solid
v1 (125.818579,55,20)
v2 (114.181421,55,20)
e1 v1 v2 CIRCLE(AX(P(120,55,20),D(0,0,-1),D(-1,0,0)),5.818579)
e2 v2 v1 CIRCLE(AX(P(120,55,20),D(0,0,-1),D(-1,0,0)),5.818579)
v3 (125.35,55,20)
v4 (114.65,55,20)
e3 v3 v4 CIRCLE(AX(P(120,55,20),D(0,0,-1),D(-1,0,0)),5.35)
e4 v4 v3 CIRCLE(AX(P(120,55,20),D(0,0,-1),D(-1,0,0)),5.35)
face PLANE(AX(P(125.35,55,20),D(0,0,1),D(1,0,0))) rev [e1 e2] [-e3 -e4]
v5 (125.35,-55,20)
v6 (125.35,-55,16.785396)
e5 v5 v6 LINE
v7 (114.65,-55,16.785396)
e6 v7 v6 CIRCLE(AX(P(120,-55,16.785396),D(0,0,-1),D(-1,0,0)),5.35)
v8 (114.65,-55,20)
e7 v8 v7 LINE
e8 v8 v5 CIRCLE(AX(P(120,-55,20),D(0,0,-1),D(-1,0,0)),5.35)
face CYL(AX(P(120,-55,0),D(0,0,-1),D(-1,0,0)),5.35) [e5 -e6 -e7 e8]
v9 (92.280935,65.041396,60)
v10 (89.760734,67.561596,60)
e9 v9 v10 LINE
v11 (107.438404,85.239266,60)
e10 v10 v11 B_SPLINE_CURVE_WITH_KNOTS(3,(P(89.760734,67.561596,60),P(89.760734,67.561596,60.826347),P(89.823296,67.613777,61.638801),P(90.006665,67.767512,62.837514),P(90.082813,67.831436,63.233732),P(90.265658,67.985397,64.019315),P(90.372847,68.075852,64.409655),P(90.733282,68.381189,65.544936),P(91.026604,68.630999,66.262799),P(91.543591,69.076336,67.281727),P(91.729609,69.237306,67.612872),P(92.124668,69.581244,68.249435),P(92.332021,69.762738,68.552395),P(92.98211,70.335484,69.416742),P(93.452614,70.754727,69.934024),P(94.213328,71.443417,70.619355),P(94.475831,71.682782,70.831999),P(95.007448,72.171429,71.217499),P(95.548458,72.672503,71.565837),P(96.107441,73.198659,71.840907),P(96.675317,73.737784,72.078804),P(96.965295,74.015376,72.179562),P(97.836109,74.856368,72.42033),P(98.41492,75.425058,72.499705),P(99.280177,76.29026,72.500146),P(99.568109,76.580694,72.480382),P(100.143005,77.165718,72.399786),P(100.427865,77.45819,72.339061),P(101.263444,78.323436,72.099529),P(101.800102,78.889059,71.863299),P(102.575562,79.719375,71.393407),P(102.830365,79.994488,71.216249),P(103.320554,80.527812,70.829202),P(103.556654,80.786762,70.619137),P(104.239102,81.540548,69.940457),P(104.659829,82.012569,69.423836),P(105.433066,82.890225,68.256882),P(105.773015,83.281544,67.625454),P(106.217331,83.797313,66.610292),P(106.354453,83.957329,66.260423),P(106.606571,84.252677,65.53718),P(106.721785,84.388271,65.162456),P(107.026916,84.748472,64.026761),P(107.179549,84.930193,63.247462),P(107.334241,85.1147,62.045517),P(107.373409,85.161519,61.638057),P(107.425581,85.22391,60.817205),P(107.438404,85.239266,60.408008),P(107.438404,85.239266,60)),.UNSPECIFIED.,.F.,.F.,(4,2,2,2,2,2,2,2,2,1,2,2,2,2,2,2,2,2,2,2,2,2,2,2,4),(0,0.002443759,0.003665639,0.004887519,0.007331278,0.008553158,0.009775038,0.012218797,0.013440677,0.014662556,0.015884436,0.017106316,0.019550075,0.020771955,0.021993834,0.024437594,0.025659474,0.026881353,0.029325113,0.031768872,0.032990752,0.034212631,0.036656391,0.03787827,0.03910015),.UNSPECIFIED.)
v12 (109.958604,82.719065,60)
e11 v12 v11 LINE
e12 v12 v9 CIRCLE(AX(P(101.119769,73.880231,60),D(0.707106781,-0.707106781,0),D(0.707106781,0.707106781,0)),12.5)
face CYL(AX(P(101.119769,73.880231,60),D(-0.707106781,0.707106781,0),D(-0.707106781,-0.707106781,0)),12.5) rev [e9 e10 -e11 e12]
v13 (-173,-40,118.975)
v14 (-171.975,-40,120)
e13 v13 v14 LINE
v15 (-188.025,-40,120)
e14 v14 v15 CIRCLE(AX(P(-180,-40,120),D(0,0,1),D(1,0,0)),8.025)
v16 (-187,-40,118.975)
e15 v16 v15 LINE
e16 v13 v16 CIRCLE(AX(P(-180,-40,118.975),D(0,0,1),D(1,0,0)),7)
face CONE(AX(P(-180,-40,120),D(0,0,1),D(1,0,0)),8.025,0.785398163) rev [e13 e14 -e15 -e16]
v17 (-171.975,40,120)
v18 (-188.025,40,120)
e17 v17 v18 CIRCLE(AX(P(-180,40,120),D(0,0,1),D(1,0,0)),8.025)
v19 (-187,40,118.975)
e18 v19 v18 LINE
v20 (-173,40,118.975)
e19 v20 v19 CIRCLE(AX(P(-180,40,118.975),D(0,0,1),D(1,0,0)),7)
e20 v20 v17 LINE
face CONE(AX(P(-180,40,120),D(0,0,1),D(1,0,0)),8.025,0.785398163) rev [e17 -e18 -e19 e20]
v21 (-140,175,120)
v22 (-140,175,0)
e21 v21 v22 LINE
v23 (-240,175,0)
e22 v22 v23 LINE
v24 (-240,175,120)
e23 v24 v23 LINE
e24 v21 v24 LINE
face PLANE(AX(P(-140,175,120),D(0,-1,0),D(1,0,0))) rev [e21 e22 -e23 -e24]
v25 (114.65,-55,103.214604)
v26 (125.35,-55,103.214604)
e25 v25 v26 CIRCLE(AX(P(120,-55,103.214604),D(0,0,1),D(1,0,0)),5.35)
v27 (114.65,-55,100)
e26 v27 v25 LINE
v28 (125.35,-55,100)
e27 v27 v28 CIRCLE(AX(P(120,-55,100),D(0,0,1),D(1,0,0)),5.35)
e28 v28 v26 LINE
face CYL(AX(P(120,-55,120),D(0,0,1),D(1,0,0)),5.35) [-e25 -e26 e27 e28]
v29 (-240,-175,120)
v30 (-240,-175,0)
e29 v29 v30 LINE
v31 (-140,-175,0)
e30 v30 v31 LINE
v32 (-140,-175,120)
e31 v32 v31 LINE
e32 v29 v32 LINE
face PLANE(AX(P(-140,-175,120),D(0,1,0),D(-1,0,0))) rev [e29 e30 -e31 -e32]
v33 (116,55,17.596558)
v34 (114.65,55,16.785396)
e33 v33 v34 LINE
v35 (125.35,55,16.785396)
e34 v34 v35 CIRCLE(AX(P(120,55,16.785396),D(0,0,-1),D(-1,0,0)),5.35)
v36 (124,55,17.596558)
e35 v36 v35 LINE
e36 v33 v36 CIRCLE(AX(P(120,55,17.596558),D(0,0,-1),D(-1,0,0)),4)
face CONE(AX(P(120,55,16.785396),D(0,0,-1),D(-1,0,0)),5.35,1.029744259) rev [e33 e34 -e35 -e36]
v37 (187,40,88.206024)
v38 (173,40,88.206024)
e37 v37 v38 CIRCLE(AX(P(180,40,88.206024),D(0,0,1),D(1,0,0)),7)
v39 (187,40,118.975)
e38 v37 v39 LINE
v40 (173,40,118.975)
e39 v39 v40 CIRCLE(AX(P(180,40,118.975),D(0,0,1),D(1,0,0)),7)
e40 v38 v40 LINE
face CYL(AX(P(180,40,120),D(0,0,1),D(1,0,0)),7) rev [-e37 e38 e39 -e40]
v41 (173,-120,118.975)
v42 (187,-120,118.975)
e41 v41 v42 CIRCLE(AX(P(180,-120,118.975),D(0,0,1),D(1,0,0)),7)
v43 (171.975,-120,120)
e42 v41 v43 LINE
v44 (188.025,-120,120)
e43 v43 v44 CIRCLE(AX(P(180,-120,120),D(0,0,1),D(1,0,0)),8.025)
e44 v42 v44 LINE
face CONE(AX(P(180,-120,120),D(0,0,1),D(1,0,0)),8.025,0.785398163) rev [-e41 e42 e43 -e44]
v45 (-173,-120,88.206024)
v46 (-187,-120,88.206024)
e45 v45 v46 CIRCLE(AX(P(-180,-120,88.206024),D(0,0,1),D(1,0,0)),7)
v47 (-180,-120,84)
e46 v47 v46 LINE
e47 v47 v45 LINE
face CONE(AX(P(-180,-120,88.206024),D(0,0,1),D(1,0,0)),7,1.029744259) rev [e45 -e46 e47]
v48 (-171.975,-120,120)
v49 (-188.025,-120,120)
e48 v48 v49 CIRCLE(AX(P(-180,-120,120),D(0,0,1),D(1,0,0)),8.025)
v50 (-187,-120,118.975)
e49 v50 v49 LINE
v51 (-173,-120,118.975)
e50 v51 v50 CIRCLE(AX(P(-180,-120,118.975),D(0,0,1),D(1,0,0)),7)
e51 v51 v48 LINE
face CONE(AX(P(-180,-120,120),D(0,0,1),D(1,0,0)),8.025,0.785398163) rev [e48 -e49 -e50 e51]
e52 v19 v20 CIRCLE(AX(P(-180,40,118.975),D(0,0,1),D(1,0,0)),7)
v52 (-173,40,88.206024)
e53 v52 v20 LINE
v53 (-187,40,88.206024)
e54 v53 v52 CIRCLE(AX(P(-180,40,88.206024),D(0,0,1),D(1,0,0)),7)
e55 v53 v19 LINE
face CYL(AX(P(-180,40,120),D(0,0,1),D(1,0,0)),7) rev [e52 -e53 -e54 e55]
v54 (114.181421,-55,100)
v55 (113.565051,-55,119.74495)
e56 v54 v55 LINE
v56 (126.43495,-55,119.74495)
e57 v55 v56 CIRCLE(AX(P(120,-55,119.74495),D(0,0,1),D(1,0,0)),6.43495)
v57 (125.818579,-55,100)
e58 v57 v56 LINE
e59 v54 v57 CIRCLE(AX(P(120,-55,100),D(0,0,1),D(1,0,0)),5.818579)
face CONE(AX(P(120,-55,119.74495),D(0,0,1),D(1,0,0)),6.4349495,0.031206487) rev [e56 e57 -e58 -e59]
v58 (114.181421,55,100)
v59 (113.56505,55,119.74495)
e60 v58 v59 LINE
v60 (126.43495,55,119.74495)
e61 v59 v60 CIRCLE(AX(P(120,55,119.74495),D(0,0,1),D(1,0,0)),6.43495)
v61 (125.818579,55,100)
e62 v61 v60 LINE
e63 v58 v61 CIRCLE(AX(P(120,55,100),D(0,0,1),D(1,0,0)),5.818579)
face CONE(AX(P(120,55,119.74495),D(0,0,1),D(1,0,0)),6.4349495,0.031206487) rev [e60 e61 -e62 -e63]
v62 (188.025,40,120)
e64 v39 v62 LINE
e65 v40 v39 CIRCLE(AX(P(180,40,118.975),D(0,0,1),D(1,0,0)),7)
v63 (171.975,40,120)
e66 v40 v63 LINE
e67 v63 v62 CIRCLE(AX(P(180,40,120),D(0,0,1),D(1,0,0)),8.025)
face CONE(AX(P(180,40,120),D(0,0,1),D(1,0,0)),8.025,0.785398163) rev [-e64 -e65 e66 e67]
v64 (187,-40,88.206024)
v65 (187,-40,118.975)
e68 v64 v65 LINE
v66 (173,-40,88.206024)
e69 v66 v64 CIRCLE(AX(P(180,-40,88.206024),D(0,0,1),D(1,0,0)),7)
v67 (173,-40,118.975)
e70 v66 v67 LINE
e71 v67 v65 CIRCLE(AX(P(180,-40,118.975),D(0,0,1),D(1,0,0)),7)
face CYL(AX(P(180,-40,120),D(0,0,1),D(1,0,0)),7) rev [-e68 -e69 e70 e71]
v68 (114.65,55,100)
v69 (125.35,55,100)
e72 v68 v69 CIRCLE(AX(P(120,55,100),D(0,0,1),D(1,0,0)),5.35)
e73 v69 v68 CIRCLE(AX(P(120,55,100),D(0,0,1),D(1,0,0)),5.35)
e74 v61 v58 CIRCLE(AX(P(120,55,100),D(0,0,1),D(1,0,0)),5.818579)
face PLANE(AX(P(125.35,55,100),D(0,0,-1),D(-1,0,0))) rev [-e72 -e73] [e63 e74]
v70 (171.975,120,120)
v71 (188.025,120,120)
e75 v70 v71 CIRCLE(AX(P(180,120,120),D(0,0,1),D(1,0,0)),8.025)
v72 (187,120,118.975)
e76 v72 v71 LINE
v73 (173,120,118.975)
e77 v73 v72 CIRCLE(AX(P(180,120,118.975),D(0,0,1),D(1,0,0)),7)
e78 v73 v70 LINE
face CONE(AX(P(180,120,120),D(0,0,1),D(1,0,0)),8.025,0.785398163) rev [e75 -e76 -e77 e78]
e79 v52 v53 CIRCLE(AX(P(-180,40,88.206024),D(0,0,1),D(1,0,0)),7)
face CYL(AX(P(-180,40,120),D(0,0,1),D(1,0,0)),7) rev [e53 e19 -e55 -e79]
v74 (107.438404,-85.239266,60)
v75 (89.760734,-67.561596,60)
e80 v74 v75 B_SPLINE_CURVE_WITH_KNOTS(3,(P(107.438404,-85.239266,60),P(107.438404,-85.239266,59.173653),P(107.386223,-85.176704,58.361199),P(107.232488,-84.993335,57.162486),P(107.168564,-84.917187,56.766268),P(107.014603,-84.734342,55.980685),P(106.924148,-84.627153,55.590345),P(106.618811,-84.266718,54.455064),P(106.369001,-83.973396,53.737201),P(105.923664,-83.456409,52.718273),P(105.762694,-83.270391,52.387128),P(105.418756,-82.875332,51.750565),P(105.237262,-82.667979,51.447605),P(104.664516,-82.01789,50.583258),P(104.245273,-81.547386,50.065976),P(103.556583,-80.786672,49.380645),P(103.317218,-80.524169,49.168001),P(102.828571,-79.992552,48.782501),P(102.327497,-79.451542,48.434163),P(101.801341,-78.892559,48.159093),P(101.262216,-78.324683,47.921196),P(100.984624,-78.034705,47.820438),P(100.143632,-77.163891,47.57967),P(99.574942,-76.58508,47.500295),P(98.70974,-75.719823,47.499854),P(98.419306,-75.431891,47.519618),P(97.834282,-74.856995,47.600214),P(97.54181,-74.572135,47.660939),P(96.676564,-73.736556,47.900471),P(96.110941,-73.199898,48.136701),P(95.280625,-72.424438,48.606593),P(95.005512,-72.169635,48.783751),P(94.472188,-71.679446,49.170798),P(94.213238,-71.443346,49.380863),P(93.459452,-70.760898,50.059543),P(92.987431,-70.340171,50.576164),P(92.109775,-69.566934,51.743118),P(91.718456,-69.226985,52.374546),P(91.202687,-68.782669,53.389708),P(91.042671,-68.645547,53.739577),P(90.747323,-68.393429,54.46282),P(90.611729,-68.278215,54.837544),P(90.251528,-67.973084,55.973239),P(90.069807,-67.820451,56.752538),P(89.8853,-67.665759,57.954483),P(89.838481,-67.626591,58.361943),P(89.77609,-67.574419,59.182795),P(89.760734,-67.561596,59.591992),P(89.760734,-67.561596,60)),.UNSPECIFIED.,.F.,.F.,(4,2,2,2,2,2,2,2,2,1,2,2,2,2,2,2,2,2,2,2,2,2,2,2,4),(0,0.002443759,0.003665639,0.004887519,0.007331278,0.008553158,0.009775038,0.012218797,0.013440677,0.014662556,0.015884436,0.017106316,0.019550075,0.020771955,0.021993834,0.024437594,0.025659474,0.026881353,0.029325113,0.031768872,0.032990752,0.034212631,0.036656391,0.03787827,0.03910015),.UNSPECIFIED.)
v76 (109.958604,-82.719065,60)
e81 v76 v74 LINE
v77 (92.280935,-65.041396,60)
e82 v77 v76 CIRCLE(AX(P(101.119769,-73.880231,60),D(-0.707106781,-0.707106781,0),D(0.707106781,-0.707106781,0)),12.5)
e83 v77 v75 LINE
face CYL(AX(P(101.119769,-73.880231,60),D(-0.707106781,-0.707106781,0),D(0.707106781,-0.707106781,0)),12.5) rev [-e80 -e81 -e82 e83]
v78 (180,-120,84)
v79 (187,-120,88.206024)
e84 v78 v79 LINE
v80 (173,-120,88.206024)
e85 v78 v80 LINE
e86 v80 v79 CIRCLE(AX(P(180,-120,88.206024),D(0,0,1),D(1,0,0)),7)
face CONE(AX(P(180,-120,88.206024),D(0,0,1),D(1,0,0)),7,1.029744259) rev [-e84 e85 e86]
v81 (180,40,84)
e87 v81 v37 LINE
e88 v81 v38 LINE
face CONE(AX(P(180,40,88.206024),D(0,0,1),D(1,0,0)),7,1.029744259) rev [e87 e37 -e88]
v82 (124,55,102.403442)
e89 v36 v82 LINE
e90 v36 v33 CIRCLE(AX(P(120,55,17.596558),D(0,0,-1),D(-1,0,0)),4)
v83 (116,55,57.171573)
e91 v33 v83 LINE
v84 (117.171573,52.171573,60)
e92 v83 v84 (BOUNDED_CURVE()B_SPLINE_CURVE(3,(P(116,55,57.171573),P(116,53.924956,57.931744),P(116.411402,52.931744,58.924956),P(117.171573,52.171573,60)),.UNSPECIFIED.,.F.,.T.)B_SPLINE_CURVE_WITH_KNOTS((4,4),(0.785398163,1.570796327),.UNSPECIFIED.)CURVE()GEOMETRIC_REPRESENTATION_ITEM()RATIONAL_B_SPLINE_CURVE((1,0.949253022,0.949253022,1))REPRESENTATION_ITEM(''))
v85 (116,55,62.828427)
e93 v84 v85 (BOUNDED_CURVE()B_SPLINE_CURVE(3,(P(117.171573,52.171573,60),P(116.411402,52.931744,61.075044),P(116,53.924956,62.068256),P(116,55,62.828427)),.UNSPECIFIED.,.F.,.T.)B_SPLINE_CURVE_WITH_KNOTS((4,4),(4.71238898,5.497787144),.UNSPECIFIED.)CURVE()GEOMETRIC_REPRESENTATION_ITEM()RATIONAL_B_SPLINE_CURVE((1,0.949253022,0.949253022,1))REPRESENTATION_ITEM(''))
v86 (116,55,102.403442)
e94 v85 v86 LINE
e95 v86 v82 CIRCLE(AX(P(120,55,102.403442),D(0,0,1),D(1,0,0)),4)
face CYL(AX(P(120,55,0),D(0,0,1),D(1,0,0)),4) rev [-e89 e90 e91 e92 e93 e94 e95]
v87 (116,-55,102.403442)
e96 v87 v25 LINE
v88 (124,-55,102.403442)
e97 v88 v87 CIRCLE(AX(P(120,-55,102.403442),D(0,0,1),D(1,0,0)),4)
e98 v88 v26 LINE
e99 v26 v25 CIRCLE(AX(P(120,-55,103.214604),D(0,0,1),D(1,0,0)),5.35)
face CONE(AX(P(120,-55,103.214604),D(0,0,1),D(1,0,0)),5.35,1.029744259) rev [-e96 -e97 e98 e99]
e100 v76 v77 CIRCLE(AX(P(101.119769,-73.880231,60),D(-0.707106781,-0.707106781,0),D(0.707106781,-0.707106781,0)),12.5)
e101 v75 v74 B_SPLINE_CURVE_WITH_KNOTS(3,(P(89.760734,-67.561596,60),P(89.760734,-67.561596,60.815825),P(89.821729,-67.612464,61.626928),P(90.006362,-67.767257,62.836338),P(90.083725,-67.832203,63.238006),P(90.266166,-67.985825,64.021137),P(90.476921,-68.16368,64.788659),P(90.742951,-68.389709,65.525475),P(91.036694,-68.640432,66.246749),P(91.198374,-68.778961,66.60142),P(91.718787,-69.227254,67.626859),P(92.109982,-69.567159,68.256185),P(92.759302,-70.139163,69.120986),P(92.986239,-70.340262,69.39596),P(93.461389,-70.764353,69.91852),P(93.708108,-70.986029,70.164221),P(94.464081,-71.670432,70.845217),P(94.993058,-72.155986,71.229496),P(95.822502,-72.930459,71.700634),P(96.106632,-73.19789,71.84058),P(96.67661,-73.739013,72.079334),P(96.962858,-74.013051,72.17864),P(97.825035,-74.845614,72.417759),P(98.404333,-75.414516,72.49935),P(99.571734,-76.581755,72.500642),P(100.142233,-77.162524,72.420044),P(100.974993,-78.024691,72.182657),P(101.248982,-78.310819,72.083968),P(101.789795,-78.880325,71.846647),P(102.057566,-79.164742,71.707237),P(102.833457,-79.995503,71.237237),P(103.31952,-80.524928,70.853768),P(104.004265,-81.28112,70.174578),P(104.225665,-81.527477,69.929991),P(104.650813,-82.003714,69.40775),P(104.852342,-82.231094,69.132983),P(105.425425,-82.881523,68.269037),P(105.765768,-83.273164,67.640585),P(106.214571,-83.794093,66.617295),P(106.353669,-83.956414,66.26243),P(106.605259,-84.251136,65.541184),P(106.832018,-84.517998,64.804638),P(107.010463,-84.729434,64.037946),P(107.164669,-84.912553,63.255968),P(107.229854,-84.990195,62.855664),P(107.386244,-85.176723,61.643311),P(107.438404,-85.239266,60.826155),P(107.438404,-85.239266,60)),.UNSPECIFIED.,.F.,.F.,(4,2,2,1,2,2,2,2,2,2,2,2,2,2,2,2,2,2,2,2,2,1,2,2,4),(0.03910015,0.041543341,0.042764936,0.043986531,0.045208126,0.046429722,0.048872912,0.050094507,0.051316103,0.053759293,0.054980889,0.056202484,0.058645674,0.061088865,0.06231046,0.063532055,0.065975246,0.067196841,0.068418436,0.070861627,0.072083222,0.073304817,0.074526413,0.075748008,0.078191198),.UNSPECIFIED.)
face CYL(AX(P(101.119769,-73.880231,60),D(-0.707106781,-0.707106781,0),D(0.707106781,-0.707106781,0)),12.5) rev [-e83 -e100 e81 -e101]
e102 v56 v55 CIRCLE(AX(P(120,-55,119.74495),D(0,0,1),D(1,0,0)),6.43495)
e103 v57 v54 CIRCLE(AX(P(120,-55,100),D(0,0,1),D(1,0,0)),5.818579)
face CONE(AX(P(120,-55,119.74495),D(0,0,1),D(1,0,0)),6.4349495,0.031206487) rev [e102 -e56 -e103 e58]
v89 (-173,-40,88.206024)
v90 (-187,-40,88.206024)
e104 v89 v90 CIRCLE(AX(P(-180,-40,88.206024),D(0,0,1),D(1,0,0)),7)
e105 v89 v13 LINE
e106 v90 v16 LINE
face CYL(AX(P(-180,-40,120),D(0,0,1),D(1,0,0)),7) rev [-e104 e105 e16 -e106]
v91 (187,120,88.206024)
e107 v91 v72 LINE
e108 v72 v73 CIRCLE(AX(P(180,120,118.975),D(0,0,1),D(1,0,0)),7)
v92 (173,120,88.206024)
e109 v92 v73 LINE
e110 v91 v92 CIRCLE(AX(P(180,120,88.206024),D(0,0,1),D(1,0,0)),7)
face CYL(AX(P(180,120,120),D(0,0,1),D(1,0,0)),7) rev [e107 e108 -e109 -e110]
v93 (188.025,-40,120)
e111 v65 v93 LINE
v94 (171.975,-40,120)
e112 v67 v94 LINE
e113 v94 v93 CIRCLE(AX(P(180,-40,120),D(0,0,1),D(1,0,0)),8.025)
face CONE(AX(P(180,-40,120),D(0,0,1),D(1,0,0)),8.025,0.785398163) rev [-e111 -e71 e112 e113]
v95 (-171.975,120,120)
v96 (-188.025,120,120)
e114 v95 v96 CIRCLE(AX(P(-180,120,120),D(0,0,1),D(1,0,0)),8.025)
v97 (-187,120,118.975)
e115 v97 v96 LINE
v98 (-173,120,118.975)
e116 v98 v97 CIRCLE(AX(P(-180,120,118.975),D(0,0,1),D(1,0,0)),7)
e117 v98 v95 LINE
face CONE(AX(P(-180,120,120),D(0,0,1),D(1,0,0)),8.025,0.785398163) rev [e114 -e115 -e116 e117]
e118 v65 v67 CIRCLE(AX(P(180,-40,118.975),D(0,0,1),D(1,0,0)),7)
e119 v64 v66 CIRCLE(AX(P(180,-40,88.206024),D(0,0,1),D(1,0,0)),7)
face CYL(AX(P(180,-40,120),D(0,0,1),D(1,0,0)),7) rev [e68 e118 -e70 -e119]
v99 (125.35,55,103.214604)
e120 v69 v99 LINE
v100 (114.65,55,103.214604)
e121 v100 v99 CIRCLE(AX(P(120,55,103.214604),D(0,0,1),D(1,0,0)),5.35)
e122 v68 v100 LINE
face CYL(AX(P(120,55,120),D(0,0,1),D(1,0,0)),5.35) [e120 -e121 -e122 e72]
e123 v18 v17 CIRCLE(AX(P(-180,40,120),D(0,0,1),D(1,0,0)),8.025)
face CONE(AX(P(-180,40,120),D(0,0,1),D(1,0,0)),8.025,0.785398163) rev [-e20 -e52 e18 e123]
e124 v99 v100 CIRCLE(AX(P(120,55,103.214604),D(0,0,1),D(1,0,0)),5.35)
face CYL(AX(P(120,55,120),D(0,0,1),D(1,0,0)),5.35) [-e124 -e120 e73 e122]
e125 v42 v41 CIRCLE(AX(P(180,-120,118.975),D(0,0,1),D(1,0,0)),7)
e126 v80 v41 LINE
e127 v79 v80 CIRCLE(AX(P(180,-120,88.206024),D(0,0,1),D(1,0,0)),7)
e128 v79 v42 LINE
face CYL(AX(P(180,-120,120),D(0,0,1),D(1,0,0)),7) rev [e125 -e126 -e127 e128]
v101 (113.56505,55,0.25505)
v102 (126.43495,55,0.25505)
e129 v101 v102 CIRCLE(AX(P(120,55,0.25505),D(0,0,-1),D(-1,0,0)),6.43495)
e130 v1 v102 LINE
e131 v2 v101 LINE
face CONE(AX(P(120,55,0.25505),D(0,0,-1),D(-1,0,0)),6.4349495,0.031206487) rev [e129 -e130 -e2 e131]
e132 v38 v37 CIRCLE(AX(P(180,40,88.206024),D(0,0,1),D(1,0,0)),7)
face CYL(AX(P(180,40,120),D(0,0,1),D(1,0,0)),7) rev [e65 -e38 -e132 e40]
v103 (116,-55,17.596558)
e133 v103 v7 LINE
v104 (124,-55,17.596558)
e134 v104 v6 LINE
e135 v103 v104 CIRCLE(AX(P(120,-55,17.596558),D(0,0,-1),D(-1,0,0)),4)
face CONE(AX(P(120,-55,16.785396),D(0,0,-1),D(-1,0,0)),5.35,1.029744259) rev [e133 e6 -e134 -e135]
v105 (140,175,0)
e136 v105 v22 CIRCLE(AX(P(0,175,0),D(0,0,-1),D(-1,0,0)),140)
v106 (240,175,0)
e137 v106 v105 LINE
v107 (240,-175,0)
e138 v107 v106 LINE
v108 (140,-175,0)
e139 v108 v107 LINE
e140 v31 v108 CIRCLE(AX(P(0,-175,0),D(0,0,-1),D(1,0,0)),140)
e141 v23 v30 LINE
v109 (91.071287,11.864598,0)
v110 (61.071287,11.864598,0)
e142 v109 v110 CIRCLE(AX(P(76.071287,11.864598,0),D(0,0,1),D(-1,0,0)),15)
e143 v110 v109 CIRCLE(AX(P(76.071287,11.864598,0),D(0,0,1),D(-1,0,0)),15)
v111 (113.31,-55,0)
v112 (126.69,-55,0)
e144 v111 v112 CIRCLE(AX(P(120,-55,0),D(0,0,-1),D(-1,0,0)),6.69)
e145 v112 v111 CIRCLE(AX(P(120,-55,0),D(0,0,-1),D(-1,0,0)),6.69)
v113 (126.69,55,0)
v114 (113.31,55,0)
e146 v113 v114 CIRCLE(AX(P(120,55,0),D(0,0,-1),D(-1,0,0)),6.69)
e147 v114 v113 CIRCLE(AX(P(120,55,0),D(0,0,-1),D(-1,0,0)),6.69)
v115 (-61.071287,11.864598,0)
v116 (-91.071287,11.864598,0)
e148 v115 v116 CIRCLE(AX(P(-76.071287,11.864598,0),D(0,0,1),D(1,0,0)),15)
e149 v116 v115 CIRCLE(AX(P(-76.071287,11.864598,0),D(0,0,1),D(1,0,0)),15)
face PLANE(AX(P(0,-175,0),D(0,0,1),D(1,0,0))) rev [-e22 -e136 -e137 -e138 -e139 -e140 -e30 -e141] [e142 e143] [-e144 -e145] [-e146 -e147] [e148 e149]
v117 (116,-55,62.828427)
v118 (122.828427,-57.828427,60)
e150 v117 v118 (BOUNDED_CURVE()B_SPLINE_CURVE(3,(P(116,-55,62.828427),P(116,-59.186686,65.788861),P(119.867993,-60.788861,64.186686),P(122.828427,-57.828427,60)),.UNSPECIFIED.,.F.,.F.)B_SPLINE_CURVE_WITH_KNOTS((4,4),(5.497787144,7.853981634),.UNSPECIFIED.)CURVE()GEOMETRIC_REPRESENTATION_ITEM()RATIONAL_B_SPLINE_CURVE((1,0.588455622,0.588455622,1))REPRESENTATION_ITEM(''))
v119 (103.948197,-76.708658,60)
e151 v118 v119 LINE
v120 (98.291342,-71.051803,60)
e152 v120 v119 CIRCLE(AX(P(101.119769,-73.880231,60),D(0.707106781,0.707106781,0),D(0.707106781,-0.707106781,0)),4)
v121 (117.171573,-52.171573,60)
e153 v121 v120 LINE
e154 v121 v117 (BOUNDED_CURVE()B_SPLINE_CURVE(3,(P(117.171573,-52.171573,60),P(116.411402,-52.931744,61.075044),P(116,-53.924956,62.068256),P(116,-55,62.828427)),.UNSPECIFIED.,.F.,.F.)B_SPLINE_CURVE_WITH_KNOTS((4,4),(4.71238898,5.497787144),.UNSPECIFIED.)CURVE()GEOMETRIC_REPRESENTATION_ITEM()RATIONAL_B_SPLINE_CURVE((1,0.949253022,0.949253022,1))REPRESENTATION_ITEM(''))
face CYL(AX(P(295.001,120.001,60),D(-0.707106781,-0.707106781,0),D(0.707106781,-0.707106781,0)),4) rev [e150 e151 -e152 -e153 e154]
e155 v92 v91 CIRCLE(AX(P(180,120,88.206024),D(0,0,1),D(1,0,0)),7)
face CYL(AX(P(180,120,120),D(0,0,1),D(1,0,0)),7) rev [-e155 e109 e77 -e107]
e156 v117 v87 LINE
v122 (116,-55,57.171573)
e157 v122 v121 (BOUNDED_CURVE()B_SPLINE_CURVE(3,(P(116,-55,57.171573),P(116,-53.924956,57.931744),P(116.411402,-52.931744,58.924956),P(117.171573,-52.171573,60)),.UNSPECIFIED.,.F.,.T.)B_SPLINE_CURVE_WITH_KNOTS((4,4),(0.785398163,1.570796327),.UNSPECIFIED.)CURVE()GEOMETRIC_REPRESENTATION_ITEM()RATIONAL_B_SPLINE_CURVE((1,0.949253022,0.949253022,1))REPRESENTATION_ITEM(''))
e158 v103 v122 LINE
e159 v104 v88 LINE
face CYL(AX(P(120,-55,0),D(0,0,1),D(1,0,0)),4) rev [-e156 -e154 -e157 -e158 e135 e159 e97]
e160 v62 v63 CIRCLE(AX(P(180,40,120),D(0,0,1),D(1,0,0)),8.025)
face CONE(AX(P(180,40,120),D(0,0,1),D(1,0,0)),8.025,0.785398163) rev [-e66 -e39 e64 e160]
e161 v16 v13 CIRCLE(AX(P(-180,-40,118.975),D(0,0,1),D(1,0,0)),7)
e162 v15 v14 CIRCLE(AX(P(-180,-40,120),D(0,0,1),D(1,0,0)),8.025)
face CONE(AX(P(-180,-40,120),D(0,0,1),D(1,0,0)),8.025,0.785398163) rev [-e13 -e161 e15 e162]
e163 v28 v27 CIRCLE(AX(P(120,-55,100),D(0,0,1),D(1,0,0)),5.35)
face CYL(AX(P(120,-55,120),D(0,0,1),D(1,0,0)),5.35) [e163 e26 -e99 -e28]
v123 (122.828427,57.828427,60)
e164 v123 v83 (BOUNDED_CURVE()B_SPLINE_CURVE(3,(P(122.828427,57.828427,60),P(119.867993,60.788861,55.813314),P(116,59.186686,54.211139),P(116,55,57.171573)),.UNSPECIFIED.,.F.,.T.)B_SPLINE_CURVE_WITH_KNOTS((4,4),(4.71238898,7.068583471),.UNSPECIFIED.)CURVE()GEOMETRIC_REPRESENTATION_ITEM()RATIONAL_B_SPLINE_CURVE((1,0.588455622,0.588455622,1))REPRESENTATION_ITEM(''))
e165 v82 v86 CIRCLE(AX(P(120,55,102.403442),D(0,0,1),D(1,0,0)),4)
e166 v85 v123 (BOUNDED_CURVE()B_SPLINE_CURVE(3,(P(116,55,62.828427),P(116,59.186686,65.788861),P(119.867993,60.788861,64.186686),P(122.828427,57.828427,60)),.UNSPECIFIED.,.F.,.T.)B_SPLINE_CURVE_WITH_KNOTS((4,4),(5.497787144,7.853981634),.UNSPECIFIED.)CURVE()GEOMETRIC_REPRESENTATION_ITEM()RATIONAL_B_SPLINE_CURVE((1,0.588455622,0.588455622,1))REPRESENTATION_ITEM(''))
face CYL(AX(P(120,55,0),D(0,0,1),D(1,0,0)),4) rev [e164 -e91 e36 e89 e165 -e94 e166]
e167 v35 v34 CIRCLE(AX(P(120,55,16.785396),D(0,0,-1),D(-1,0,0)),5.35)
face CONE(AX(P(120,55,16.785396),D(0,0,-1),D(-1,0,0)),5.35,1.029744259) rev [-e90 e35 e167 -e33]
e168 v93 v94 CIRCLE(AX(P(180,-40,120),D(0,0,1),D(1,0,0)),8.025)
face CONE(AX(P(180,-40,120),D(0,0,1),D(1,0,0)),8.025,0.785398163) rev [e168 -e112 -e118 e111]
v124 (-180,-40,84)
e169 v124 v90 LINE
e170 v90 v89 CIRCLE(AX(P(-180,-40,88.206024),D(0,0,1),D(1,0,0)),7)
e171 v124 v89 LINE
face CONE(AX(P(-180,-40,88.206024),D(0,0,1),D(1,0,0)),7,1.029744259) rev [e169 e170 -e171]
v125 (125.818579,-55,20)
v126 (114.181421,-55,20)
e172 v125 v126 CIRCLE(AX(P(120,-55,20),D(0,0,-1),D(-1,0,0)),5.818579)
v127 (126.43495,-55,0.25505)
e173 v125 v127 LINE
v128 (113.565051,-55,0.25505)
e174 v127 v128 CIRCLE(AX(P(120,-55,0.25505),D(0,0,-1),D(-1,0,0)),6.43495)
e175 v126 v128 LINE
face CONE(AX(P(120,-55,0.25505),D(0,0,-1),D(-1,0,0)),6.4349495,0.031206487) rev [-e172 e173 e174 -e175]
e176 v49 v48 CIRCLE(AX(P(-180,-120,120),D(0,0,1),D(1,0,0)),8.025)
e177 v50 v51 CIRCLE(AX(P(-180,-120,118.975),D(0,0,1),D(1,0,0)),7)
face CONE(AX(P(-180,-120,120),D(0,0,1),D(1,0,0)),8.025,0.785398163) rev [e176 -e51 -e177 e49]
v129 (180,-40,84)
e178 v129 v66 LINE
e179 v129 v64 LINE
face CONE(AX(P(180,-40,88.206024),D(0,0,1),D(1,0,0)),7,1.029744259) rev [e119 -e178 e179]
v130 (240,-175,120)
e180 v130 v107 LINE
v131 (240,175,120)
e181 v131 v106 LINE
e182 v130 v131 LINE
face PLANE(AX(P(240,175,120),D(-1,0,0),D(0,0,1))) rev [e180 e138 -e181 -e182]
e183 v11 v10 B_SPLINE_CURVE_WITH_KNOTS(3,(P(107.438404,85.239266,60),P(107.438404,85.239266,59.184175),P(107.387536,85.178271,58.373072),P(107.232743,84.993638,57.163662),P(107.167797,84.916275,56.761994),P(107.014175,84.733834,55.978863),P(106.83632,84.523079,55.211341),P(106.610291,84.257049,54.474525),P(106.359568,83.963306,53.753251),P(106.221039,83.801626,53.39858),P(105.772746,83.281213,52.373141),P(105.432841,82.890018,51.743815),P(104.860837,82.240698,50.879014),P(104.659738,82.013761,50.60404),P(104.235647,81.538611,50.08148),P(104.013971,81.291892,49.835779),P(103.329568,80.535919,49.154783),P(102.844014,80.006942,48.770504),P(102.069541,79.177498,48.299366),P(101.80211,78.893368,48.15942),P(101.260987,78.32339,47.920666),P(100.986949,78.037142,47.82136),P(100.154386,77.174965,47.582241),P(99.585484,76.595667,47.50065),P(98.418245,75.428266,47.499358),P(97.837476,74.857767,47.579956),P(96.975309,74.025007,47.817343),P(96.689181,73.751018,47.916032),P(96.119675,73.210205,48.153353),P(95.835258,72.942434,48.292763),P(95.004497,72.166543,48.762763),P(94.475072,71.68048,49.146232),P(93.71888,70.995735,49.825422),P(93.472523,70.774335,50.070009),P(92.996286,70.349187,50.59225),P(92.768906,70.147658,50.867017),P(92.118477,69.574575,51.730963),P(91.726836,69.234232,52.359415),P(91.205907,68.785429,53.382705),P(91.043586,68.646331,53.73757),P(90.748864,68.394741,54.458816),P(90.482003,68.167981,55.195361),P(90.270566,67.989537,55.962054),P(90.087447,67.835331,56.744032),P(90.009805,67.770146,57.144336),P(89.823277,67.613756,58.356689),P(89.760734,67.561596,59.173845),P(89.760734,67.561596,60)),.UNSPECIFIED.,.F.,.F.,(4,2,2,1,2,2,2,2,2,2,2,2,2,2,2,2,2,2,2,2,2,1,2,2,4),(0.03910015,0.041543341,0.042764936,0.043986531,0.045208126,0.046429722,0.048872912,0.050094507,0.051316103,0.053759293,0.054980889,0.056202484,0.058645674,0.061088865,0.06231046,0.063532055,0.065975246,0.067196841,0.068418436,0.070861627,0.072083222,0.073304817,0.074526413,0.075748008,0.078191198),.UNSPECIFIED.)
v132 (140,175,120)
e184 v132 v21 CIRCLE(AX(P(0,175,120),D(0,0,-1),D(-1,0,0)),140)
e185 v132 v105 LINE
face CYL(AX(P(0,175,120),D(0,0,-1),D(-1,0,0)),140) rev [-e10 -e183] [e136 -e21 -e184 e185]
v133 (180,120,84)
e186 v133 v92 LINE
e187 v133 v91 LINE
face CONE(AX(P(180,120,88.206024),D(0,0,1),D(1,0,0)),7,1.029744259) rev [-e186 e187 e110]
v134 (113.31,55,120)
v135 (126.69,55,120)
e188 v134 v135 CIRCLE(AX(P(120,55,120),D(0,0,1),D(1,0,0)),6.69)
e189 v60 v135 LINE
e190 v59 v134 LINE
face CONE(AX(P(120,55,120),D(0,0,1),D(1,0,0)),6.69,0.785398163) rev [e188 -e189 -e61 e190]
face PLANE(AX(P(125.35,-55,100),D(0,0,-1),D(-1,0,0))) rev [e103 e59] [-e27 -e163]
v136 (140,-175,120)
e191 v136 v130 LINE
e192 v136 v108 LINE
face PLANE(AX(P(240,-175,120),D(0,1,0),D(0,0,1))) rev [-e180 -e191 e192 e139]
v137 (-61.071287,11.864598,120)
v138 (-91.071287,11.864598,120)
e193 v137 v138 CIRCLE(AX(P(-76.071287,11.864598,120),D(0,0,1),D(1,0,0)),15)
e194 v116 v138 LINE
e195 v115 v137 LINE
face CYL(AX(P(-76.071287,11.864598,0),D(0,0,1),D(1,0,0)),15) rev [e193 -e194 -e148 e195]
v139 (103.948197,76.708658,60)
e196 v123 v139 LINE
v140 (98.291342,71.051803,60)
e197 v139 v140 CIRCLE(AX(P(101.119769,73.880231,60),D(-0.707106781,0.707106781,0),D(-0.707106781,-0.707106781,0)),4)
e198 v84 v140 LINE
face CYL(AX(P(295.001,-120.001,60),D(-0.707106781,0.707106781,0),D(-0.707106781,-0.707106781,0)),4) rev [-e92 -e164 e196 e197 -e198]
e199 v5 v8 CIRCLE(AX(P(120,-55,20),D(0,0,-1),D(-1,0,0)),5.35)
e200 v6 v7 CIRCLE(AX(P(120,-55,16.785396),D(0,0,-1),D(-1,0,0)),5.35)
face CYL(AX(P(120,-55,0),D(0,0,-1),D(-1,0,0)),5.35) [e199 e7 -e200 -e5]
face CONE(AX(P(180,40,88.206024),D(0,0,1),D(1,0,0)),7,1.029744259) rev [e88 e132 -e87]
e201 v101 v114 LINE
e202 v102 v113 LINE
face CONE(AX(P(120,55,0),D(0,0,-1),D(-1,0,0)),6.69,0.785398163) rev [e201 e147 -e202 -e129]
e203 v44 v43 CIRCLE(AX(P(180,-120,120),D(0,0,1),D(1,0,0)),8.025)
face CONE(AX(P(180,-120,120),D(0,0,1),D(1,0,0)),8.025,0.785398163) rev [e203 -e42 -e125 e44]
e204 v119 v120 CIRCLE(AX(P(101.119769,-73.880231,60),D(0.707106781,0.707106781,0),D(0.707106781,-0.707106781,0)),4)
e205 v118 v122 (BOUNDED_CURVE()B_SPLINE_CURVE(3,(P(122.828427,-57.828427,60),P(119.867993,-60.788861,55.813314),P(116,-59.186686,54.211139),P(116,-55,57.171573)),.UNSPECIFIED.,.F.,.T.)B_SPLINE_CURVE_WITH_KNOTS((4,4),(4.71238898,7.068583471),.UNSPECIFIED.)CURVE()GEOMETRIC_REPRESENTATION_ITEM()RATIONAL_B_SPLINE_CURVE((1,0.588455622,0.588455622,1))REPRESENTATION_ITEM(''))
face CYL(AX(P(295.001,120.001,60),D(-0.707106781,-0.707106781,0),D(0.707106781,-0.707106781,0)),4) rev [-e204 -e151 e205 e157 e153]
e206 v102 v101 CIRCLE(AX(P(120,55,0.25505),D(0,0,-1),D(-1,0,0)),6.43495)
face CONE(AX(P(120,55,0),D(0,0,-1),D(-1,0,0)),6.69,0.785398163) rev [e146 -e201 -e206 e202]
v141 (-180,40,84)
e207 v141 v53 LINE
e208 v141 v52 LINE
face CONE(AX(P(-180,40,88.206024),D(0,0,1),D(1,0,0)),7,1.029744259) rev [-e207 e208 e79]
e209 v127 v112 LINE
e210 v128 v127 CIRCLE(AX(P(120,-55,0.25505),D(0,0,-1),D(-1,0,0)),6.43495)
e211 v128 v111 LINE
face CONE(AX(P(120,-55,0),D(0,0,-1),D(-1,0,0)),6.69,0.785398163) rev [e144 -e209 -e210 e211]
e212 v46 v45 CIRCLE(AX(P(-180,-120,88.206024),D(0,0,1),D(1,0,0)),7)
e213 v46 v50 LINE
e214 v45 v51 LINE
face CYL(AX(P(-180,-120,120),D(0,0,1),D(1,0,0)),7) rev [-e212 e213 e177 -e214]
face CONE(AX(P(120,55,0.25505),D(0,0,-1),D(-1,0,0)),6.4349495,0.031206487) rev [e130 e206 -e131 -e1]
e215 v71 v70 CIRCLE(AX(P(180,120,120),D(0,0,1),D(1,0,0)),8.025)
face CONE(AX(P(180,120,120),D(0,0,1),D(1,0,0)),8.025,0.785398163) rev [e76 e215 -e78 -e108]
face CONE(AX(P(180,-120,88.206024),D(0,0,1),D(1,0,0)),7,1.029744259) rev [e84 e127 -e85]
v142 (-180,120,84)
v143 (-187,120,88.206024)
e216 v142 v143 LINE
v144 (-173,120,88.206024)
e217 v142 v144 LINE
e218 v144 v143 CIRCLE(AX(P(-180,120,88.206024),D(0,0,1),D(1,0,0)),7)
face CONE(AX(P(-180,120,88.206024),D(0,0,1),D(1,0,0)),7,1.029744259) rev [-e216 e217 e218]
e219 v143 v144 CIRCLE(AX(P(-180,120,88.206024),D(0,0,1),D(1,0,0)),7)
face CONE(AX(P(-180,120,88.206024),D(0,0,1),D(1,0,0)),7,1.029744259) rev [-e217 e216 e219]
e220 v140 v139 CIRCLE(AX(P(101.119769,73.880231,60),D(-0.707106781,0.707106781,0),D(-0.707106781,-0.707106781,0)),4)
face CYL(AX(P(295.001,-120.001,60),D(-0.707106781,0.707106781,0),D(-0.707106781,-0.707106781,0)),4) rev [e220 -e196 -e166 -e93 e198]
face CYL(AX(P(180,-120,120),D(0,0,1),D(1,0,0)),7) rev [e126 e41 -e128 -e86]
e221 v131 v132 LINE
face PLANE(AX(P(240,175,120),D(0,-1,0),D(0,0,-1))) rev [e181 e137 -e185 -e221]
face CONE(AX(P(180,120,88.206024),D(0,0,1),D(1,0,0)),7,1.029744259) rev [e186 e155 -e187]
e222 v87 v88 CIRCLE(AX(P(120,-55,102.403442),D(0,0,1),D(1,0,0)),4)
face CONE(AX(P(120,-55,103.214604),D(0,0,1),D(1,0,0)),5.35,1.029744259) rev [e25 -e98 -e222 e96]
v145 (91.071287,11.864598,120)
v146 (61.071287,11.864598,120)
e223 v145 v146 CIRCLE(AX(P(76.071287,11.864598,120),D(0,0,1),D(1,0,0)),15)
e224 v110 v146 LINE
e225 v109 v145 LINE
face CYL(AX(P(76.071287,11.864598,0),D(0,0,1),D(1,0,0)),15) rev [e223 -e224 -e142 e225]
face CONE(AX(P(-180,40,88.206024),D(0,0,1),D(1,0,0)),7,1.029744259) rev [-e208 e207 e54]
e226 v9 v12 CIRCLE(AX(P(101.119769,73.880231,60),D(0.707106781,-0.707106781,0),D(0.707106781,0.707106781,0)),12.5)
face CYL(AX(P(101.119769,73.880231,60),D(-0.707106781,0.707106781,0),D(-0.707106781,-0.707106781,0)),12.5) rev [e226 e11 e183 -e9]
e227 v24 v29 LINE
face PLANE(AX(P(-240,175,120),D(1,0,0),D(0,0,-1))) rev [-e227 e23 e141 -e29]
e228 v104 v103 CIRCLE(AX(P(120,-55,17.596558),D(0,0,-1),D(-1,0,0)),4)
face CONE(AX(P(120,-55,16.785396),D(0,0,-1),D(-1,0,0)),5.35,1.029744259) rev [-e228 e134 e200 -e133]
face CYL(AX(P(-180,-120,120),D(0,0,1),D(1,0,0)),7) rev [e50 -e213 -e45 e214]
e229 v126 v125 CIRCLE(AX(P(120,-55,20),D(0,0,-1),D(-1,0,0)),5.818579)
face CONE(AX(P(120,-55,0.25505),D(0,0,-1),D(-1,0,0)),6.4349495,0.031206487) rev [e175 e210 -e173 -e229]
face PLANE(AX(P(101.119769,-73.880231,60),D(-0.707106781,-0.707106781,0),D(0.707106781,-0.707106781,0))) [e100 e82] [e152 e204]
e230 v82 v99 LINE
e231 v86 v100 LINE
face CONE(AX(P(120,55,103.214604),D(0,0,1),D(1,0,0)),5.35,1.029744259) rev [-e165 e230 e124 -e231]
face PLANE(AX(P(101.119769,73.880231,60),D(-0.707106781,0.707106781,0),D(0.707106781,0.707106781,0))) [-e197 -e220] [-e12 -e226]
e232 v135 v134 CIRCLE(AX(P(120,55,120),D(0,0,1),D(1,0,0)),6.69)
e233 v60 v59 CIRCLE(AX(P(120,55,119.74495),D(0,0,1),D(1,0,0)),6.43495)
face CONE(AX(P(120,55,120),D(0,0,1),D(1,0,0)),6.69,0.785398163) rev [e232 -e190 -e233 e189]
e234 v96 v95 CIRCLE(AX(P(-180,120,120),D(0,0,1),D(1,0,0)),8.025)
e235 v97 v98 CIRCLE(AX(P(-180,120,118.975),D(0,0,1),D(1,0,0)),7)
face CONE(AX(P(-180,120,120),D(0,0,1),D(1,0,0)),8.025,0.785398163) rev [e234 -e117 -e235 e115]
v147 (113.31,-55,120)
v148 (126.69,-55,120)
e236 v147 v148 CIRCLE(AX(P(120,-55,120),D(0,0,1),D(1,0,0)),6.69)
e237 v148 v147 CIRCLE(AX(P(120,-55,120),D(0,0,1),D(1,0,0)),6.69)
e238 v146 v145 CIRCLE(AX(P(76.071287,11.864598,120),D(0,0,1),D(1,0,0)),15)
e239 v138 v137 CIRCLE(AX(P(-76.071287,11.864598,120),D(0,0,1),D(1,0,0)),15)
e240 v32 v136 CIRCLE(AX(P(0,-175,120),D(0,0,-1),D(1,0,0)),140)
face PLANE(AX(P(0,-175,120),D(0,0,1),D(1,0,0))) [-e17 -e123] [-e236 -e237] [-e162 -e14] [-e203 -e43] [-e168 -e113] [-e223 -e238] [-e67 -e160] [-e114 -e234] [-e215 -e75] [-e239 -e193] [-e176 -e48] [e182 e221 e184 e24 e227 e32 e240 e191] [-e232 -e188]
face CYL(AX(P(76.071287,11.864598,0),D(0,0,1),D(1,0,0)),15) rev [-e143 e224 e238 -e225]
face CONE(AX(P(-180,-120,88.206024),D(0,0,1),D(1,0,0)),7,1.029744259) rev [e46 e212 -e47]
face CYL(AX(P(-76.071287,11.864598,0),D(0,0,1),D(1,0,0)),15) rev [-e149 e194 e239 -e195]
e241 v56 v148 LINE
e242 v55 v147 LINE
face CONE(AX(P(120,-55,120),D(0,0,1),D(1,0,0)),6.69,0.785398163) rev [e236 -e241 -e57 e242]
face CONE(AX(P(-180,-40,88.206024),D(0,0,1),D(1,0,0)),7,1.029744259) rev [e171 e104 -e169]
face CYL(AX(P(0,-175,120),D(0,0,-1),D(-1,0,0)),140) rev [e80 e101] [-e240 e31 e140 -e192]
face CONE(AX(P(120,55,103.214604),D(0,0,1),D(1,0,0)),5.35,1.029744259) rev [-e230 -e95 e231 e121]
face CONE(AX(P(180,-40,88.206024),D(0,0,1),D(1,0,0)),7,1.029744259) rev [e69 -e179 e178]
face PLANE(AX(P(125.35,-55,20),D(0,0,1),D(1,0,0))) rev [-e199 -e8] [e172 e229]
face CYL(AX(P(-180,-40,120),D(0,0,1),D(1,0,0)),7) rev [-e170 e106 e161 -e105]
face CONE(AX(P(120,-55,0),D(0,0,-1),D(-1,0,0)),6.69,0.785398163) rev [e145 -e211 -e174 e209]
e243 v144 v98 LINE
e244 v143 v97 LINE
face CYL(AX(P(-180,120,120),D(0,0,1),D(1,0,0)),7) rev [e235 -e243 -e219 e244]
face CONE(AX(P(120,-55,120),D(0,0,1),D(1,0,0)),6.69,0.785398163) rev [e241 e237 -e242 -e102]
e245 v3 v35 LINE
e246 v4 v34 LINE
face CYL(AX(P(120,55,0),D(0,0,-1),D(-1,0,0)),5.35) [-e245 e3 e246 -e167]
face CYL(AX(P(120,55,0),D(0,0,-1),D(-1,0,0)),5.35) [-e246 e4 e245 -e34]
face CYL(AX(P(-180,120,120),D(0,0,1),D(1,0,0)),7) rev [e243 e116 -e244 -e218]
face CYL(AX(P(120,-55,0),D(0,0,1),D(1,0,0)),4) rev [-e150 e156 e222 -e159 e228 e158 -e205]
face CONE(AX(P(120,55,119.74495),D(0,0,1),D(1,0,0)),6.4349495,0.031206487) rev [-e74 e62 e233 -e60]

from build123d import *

# Parameters (mm, degrees)
EXTRUDE_1_DEPTH               = 120
HOLE_WIZARD_M16_1_D           = 14
HOLE_WIZARD_M16_1_DEPTH       = 31.793975667
HOLE_WIZARD_M16_1_CSINK_D     = 16.05
HOLE_WIZARD_M16_1_CSINK_ANGLE = 90
HOLE_WIZARD_M16_1_TIP         = 4.206024333
CUT_EXTRUDE_1_DEPTH           = 321.351369593
CUT_EXTRUDE_1_DEPTH_BACK      = 321.351369593
SKETCH_5_R                    = 15
CUT_EXTRUDE_2_DEPTH           = 321.351369593
CUT_EXTRUDE_2_DEPTH_BACK      = 321.351369593
SKETCH_6_R                    = 4
F_1_4_RC_1_AT_2_COUNT         = 2
F_1_4_RC_1_AT_2_PITCH         = 110
F_1_4_RC_2_AT_2_COUNT         = 2
F_1_4_RC_2_AT_2_PITCH         = 110
CUT_EXTRUDE_3_REACH           = 345.165
CUT_EXTRUDE_3_END_RADIUS      = 4
SKETCH_12_R                   = 4
SKETCH_14_R                   = 12.5
CUT_EXTRUDE_4_DEPTH           = 44.01


with BuildPart() as part:
    # 草图1 → 凸台-拉伸1 (new body)
    with BuildSketch(Plane.XY):
        with BuildLine():
            Line((-140, -175), (-240, -175))
            Line((-240, -175), (-240, 175))
            Line((-240, 175), (-140, 175))
            ThreePointArc((-140, 175), (0, 35), (140, 175))
            Line((140, 175), (240, 175))
            Line((240, 175), (240, -175))
            Line((240, -175), (140, -175))
            ThreePointArc((140, -175), (0, -35), (-140, -175))
        make_face()
    extrude(amount=EXTRUDE_1_DEPTH)

    # M16 螺纹孔1
    with Locations(Plane.XY.offset(120)):
        with Locations((-180, 120), (-180, 40), (-180, -40), (-180, -120), (180, -120), (180, -40), (180, 40), (180, 120)):
            CounterSinkHole(HOLE_WIZARD_M16_1_D / 2, HOLE_WIZARD_M16_1_CSINK_D / 2, depth=HOLE_WIZARD_M16_1_DEPTH, counter_sink_angle=HOLE_WIZARD_M16_1_CSINK_ANGLE)
            with Locations((0, 0, -(HOLE_WIZARD_M16_1_DEPTH + HOLE_WIZARD_M16_1_TIP / 2))):  # 118° drill point
                Cone(0, HOLE_WIZARD_M16_1_D / 2, HOLE_WIZARD_M16_1_TIP, mode=Mode.SUBTRACT)

    # 草图5 → 切除-拉伸1 (cut, two sides: drawn at the far end of the back side and taken through both)
    with BuildSketch(Plane.XY.offset(120).offset(-CUT_EXTRUDE_1_DEPTH_BACK)):
        with Locations((-76.071287113, 11.864598333)):
            Circle(SKETCH_5_R)
        with Locations((76.071287113, 11.864598333)):
            Circle(SKETCH_5_R)
    extrude(amount=CUT_EXTRUDE_1_DEPTH + CUT_EXTRUDE_1_DEPTH_BACK, mode=Mode.SUBTRACT)

    # 草图6 → 切除-拉伸2 (cut, two sides: drawn at the far end of the back side and taken through both)
    with BuildSketch(Plane.XY.offset(120).offset(-CUT_EXTRUDE_2_DEPTH_BACK)):
        with Locations((120, 55)):
            Circle(SKETCH_6_R)
        with Locations((120, -55)):
            Circle(SKETCH_6_R)
    extrude(amount=CUT_EXTRUDE_2_DEPTH + CUT_EXTRUDE_2_DEPTH_BACK, mode=Mode.SUBTRACT)

    # 草图8 → 1/4 Rc 螺纹孔1 (revolve, cut)
    with BuildSketch(Plane(origin=(120, 55, 120), x_dir=(0, -1, 0), z_dir=(1, 0, 0))):
        Polygon((0, 0), (0, 20), (5.35, 16.785395688), (5.35, 20), (5.818578894, 20), (6.4349495, 0.2550505), (6.69, 0), align=None)
    f_1_4_rc_1 = revolve(axis=Axis((120, 55, 126.35), (0, 0, -1)), mode=Mode.SUBTRACT)

    # 1/4 Rc 螺纹孔1 at 2: 1/4 Rc 螺纹孔1 ×2
    with Locations(*[(0, -i * F_1_4_RC_1_AT_2_PITCH, 0) for i in range(1, F_1_4_RC_1_AT_2_COUNT)]):
        add(f_1_4_rc_1, mode=Mode.SUBTRACT)

    # 草图10 → 1/4 Rc 螺纹孔2 (revolve, cut)
    with BuildSketch(Plane(origin=(120, 55, 0), x_dir=(0, 1, 0), z_dir=(1, 0, 0))):
        Polygon((0, 0), (0, 20), (5.35, 16.785395688), (5.35, 20), (5.818578894, 20), (6.4349495, 0.2550505), (6.69, 0), align=None)
    f_1_4_rc_2 = revolve(axis=Axis((120, 55, -6.35), (0, 0, 1)), mode=Mode.SUBTRACT)

    # 1/4 Rc 螺纹孔2 at 2: 1/4 Rc 螺纹孔2 ×2
    with Locations(*[(0, -i * F_1_4_RC_2_AT_2_PITCH, 0) for i in range(1, F_1_4_RC_2_AT_2_COUNT)]):
        add(f_1_4_rc_2, mode=Mode.SUBTRACT)

    # 切除-拉伸3: up to this cylinder (the profile starts outside it)
    cut_extrude_3_end = Plane(origin=(120, -55, 60), z_dir=(0, 0, 1)) * Cylinder(CUT_EXTRUDE_3_END_RADIUS, 699.33, mode=Mode.PRIVATE)
    # 草图12 → 切除-拉伸3 (cut, up to the surface)
    with BuildSketch(Plane(origin=(-17.5, -17.5, 0), x_dir=(0, 0, -1), z_dir=(-0.7071067811865488, -0.7071067811865464, 0)), mode=Mode.PRIVATE) as cut_extrude_3_sk1:
        with Locations(Location((-60, 123.743686708, 0), (0, 0, 90))):
            Circle(SKETCH_12_R)
    cut_extrude_3_tool1 = extrude(cut_extrude_3_sk1.sketch, amount=-CUT_EXTRUDE_3_REACH, mode=Mode.PRIVATE) - cut_extrude_3_end
    cut_extrude_3 = cut_extrude_3_tool1.solids().sort_by_distance((70, -105, 60))[0]
    add(cut_extrude_3, mode=Mode.SUBTRACT)

    # 草图14 → 切除-拉伸4 (cut)
    with BuildSketch(Plane(origin=(-17.5, -17.5, 0), x_dir=(0, 0, -1), z_dir=(-0.7071067811865488, -0.7071067811865464, 0))):
        with Locations(Location((-60, 123.743686708, 0), (0, 0, 90))):
            Circle(SKETCH_14_R)
    cut_extrude_4 = extrude(amount=-CUT_EXTRUDE_4_DEPTH, mode=Mode.SUBTRACT)

    # 镜向1: 切除-拉伸3, 切除-拉伸4 across plane
    add(cut_extrude_3.mirror(Plane.ZX), mode=Mode.SUBTRACT)
    add(cut_extrude_4.mirror(Plane.ZX), mode=Mode.SUBTRACT)


solid = part.part
